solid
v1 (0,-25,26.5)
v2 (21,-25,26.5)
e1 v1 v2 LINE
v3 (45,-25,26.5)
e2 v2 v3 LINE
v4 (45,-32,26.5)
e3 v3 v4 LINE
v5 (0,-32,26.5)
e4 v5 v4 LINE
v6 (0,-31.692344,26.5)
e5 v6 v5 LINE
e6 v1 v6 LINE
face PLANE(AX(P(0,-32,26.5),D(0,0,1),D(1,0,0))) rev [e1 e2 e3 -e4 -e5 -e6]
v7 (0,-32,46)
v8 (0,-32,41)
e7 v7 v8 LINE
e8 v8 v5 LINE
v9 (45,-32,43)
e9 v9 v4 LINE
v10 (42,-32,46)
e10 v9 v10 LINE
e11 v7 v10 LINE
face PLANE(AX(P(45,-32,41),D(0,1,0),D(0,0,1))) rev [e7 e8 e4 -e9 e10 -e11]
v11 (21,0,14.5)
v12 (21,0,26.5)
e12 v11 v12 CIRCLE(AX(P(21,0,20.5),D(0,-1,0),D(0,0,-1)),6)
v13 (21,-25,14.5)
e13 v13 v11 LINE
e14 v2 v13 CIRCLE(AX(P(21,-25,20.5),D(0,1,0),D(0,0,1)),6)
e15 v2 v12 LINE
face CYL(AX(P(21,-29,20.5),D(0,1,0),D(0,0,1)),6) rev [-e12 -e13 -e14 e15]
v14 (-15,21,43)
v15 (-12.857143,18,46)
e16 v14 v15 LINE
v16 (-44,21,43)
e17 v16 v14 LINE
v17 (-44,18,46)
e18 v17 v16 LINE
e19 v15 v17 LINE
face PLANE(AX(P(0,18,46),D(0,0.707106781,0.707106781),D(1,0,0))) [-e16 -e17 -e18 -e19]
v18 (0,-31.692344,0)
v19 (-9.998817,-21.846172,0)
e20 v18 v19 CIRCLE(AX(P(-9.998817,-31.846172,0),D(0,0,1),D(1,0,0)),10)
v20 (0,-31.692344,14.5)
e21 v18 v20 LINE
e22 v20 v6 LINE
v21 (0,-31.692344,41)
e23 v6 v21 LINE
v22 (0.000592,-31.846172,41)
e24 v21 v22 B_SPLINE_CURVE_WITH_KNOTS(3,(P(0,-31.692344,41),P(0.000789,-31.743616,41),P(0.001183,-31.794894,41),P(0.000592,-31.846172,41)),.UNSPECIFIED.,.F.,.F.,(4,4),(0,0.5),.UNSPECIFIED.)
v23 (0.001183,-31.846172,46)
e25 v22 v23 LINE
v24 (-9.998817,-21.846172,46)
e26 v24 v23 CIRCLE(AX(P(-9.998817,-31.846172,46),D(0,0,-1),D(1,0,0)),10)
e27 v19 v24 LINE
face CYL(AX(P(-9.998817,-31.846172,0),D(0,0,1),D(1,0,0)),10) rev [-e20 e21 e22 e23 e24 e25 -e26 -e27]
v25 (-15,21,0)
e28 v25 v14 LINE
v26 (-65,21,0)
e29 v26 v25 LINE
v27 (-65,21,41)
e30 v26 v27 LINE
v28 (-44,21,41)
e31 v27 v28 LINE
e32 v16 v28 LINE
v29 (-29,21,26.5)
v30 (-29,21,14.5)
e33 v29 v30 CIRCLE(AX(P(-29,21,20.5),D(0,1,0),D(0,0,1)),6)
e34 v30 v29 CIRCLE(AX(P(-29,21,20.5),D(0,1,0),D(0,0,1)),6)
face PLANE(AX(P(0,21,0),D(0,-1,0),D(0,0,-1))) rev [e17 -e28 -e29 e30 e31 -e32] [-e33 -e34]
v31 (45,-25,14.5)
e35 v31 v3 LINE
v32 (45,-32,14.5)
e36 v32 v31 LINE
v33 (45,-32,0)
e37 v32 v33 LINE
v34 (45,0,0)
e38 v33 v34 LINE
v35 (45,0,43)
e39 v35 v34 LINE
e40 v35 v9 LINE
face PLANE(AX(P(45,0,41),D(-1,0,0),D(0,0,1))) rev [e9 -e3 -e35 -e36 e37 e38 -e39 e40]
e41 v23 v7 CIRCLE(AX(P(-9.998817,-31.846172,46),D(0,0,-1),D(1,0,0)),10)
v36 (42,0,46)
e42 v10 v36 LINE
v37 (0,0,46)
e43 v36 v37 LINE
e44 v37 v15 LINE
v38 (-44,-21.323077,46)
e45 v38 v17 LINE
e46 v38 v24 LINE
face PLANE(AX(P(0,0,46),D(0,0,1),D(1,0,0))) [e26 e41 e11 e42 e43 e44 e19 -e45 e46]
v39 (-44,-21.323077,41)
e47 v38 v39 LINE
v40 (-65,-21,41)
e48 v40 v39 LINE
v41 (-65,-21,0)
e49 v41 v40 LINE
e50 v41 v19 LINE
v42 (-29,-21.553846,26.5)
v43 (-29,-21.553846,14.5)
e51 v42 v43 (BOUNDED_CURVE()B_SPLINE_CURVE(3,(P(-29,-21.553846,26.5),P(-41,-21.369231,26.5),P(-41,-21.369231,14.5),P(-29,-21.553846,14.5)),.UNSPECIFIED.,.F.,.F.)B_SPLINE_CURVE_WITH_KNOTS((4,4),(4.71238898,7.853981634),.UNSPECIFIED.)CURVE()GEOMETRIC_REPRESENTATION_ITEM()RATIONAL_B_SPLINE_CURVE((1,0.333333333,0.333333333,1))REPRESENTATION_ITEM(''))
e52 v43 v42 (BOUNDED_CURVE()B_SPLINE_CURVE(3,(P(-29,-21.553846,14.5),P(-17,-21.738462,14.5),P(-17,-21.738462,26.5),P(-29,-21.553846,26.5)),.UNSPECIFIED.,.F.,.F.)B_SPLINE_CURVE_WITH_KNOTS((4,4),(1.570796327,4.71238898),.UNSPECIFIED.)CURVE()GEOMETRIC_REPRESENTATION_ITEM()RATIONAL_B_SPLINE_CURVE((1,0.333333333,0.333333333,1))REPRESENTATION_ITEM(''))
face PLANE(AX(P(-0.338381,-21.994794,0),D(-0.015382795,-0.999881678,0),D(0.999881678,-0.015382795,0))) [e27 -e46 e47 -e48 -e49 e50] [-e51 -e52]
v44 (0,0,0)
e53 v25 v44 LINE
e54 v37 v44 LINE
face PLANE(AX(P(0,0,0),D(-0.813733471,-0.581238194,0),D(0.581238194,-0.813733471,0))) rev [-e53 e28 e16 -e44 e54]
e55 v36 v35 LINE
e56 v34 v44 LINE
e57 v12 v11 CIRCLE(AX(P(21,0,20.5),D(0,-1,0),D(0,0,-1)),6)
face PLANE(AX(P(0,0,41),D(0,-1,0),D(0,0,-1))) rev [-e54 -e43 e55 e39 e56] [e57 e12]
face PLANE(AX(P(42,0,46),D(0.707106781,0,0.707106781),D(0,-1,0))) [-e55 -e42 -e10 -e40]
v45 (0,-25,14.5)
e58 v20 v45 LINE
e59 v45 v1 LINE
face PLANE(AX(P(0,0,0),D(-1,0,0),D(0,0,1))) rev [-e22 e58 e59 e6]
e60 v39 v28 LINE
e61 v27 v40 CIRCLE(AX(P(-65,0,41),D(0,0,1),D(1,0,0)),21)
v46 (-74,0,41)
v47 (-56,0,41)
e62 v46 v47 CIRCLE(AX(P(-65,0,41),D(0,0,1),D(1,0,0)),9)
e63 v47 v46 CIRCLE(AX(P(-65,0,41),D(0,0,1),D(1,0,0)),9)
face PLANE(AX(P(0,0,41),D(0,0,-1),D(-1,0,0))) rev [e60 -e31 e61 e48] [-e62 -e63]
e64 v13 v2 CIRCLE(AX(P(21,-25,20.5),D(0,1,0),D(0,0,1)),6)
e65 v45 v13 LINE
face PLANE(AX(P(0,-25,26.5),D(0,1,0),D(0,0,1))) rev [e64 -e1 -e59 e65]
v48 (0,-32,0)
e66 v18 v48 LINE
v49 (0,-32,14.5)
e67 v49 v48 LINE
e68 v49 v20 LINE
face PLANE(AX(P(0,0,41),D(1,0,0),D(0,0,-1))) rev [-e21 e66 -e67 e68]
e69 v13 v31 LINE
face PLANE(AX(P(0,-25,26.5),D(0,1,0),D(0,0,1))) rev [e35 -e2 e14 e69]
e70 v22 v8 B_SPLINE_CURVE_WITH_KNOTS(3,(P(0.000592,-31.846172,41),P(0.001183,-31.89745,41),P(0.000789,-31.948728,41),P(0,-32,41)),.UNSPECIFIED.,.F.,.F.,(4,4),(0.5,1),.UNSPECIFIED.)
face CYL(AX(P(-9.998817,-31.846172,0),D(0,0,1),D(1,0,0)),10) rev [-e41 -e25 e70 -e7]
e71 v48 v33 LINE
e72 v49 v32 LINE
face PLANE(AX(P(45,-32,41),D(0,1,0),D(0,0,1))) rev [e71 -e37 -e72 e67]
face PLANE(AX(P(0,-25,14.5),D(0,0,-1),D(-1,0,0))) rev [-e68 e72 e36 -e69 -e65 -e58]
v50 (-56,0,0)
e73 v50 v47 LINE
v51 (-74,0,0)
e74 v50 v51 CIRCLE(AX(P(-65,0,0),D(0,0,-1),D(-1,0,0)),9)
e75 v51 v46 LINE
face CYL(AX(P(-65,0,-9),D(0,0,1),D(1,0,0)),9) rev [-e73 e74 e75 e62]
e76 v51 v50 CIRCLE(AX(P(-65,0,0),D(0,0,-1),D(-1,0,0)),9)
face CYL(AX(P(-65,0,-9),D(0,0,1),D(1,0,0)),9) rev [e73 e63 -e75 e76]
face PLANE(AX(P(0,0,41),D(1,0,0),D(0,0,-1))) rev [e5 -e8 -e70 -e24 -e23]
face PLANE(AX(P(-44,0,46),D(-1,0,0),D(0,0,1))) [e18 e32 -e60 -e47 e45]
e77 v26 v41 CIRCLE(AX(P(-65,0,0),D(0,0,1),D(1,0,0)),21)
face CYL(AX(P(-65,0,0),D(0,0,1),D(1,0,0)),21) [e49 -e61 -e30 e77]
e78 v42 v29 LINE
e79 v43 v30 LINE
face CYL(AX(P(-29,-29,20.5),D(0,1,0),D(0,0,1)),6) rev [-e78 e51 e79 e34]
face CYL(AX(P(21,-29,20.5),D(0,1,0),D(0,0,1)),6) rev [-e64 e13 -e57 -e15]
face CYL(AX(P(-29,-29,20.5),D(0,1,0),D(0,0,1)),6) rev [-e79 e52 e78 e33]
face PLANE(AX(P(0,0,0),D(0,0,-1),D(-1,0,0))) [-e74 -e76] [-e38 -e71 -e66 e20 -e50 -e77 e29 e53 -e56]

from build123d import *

# Parameters (mm, degrees)
BASE_BLOCK_PROFILE_W       = 45
BASE_BLOCK_PROFILE_H       = 32
BASE_BLOCK_DEPTH           = 41
END_SLOT_PROFILE_W         = 12
END_SLOT_PROFILE_H         = 7
END_SLOT_7X12_DEPTH        = 45
ARM_EXTENSION_DEPTH        = 41
UNDERSIDE_RELIEF_PROFILE_R = 6
UNDERSIDE_RELIEF_CUT_DEPTH = 50
RAISED_START               = 5
RAISED_PAD_DEPTH           = 5
PIVOT_BORE_PROFILE_R       = 9
PIVOT_BORE_18_DEPTH        = 50
PAD_CHAMFER_3X45_A_SIZE    = 3
PAD_CHAMFER_3X45_B_SIZE    = 3


with BuildPart() as part:
    # Base Block Profile → Base Block (new body)
    with BuildSketch(Plane.XY):
        with Locations((22.5, -16)):
            Rectangle(BASE_BLOCK_PROFILE_W, BASE_BLOCK_PROFILE_H)
    extrude(amount=BASE_BLOCK_DEPTH)

    # End Slot Profile → End Slot 7x12 (cut)
    with BuildSketch(Plane(origin=(45, 0, 0), x_dir=(0, 0, -1), z_dir=(1, 0, 0))):
        with Locations((-20.5, -28.5)):
            Rectangle(END_SLOT_PROFILE_W, END_SLOT_PROFILE_H)
    extrude(amount=-END_SLOT_7X12_DEPTH, mode=Mode.SUBTRACT)

    # Arm Extension Profile → Arm Extension (add)
    with BuildSketch(Plane.XY.offset(41)):
        with BuildLine():
            Line((-15, 21), (-65, 21))
            ThreePointArc((-65, 21), (-86, 0), (-65, -21))
            Line((-65, -21), (-9.998816778, -21.84617205))
            ThreePointArc((-9.998816778, -21.84617205), (-9.844988828, -21.847355271), (-9.69119728, -21.850904657))
            ThreePointArc((-9.69119728, -21.850904657), (-2.873570133, -24.829701409), (0, -31.692344099))
            Line((0, -31.692344099), (0, -22))
            Line((0, -22), (0, 0))
            Line((0, 0), (-15, 21))
        make_face()
    extrude(amount=-ARM_EXTENSION_DEPTH)

    # Underside Relief Profile → Underside Relief Cut (cut)
    with BuildSketch(Plane(origin=(0, 21, 0), x_dir=(1, 0, 0), z_dir=(0, 1, 0))):
        with Locations(Location((-29, -20.5, 0), (0, 0, 270))):
            Circle(UNDERSIDE_RELIEF_PROFILE_R)
        with Locations(Location((21, -20.5, 0), (0, 0, 90))):
            Circle(UNDERSIDE_RELIEF_PROFILE_R)
    extrude(amount=-UNDERSIDE_RELIEF_CUT_DEPTH, mode=Mode.SUBTRACT)

    # Raised Pad Profile → Raised Pad (add)
    with BuildSketch(Plane.XY.offset(41).offset(RAISED_START)):
        with BuildLine():
            Line((-44, 21), (-44, 0))
            Line((-44, 0), (-44, -21.323076923))
            Line((-44, -21.323076923), (-9.998816778, -21.84617205))
            ThreePointArc((-9.998816778, -21.84617205), (-2.982346138, -24.720925405), (0, -31.692344099))
            ThreePointArc((0, -31.692344099), (0.001183222, -31.84617205), (0, -32))
            Line((0, -32), (45, -32))
            Line((45, -32), (45, 0))
            Line((45, 0), (0, 0))
            Line((0, 0), (-15, 21))
            Line((-15, 21), (-44, 21))
        make_face()
    extrude(amount=-RAISED_PAD_DEPTH)

    # Pivot Bore Profile → Pivot Bore Ø18 (cut)
    with BuildSketch(Plane.XY.offset(41)):
        with Locations((-65, 0)):
            Circle(PIVOT_BORE_PROFILE_R)
    extrude(amount=-PIVOT_BORE_18_DEPTH, mode=Mode.SUBTRACT)

    # Pad Chamfer 3x45 A
    pad_chamfer_3x45_a_edges = [part.edges().sort_by_distance(p)[0] for p in [
        (-29.5, 21, 46),
    ]]
    chamfer(pad_chamfer_3x45_a_edges, length=PAD_CHAMFER_3X45_A_SIZE)

    # Pad Chamfer 3x45 B
    pad_chamfer_3x45_b_edges = [part.edges().sort_by_distance(p)[0] for p in [
        (45, -16, 46),
    ]]
    chamfer(pad_chamfer_3x45_b_edges, length=PAD_CHAMFER_3X45_B_SIZE)


solid = part.part
